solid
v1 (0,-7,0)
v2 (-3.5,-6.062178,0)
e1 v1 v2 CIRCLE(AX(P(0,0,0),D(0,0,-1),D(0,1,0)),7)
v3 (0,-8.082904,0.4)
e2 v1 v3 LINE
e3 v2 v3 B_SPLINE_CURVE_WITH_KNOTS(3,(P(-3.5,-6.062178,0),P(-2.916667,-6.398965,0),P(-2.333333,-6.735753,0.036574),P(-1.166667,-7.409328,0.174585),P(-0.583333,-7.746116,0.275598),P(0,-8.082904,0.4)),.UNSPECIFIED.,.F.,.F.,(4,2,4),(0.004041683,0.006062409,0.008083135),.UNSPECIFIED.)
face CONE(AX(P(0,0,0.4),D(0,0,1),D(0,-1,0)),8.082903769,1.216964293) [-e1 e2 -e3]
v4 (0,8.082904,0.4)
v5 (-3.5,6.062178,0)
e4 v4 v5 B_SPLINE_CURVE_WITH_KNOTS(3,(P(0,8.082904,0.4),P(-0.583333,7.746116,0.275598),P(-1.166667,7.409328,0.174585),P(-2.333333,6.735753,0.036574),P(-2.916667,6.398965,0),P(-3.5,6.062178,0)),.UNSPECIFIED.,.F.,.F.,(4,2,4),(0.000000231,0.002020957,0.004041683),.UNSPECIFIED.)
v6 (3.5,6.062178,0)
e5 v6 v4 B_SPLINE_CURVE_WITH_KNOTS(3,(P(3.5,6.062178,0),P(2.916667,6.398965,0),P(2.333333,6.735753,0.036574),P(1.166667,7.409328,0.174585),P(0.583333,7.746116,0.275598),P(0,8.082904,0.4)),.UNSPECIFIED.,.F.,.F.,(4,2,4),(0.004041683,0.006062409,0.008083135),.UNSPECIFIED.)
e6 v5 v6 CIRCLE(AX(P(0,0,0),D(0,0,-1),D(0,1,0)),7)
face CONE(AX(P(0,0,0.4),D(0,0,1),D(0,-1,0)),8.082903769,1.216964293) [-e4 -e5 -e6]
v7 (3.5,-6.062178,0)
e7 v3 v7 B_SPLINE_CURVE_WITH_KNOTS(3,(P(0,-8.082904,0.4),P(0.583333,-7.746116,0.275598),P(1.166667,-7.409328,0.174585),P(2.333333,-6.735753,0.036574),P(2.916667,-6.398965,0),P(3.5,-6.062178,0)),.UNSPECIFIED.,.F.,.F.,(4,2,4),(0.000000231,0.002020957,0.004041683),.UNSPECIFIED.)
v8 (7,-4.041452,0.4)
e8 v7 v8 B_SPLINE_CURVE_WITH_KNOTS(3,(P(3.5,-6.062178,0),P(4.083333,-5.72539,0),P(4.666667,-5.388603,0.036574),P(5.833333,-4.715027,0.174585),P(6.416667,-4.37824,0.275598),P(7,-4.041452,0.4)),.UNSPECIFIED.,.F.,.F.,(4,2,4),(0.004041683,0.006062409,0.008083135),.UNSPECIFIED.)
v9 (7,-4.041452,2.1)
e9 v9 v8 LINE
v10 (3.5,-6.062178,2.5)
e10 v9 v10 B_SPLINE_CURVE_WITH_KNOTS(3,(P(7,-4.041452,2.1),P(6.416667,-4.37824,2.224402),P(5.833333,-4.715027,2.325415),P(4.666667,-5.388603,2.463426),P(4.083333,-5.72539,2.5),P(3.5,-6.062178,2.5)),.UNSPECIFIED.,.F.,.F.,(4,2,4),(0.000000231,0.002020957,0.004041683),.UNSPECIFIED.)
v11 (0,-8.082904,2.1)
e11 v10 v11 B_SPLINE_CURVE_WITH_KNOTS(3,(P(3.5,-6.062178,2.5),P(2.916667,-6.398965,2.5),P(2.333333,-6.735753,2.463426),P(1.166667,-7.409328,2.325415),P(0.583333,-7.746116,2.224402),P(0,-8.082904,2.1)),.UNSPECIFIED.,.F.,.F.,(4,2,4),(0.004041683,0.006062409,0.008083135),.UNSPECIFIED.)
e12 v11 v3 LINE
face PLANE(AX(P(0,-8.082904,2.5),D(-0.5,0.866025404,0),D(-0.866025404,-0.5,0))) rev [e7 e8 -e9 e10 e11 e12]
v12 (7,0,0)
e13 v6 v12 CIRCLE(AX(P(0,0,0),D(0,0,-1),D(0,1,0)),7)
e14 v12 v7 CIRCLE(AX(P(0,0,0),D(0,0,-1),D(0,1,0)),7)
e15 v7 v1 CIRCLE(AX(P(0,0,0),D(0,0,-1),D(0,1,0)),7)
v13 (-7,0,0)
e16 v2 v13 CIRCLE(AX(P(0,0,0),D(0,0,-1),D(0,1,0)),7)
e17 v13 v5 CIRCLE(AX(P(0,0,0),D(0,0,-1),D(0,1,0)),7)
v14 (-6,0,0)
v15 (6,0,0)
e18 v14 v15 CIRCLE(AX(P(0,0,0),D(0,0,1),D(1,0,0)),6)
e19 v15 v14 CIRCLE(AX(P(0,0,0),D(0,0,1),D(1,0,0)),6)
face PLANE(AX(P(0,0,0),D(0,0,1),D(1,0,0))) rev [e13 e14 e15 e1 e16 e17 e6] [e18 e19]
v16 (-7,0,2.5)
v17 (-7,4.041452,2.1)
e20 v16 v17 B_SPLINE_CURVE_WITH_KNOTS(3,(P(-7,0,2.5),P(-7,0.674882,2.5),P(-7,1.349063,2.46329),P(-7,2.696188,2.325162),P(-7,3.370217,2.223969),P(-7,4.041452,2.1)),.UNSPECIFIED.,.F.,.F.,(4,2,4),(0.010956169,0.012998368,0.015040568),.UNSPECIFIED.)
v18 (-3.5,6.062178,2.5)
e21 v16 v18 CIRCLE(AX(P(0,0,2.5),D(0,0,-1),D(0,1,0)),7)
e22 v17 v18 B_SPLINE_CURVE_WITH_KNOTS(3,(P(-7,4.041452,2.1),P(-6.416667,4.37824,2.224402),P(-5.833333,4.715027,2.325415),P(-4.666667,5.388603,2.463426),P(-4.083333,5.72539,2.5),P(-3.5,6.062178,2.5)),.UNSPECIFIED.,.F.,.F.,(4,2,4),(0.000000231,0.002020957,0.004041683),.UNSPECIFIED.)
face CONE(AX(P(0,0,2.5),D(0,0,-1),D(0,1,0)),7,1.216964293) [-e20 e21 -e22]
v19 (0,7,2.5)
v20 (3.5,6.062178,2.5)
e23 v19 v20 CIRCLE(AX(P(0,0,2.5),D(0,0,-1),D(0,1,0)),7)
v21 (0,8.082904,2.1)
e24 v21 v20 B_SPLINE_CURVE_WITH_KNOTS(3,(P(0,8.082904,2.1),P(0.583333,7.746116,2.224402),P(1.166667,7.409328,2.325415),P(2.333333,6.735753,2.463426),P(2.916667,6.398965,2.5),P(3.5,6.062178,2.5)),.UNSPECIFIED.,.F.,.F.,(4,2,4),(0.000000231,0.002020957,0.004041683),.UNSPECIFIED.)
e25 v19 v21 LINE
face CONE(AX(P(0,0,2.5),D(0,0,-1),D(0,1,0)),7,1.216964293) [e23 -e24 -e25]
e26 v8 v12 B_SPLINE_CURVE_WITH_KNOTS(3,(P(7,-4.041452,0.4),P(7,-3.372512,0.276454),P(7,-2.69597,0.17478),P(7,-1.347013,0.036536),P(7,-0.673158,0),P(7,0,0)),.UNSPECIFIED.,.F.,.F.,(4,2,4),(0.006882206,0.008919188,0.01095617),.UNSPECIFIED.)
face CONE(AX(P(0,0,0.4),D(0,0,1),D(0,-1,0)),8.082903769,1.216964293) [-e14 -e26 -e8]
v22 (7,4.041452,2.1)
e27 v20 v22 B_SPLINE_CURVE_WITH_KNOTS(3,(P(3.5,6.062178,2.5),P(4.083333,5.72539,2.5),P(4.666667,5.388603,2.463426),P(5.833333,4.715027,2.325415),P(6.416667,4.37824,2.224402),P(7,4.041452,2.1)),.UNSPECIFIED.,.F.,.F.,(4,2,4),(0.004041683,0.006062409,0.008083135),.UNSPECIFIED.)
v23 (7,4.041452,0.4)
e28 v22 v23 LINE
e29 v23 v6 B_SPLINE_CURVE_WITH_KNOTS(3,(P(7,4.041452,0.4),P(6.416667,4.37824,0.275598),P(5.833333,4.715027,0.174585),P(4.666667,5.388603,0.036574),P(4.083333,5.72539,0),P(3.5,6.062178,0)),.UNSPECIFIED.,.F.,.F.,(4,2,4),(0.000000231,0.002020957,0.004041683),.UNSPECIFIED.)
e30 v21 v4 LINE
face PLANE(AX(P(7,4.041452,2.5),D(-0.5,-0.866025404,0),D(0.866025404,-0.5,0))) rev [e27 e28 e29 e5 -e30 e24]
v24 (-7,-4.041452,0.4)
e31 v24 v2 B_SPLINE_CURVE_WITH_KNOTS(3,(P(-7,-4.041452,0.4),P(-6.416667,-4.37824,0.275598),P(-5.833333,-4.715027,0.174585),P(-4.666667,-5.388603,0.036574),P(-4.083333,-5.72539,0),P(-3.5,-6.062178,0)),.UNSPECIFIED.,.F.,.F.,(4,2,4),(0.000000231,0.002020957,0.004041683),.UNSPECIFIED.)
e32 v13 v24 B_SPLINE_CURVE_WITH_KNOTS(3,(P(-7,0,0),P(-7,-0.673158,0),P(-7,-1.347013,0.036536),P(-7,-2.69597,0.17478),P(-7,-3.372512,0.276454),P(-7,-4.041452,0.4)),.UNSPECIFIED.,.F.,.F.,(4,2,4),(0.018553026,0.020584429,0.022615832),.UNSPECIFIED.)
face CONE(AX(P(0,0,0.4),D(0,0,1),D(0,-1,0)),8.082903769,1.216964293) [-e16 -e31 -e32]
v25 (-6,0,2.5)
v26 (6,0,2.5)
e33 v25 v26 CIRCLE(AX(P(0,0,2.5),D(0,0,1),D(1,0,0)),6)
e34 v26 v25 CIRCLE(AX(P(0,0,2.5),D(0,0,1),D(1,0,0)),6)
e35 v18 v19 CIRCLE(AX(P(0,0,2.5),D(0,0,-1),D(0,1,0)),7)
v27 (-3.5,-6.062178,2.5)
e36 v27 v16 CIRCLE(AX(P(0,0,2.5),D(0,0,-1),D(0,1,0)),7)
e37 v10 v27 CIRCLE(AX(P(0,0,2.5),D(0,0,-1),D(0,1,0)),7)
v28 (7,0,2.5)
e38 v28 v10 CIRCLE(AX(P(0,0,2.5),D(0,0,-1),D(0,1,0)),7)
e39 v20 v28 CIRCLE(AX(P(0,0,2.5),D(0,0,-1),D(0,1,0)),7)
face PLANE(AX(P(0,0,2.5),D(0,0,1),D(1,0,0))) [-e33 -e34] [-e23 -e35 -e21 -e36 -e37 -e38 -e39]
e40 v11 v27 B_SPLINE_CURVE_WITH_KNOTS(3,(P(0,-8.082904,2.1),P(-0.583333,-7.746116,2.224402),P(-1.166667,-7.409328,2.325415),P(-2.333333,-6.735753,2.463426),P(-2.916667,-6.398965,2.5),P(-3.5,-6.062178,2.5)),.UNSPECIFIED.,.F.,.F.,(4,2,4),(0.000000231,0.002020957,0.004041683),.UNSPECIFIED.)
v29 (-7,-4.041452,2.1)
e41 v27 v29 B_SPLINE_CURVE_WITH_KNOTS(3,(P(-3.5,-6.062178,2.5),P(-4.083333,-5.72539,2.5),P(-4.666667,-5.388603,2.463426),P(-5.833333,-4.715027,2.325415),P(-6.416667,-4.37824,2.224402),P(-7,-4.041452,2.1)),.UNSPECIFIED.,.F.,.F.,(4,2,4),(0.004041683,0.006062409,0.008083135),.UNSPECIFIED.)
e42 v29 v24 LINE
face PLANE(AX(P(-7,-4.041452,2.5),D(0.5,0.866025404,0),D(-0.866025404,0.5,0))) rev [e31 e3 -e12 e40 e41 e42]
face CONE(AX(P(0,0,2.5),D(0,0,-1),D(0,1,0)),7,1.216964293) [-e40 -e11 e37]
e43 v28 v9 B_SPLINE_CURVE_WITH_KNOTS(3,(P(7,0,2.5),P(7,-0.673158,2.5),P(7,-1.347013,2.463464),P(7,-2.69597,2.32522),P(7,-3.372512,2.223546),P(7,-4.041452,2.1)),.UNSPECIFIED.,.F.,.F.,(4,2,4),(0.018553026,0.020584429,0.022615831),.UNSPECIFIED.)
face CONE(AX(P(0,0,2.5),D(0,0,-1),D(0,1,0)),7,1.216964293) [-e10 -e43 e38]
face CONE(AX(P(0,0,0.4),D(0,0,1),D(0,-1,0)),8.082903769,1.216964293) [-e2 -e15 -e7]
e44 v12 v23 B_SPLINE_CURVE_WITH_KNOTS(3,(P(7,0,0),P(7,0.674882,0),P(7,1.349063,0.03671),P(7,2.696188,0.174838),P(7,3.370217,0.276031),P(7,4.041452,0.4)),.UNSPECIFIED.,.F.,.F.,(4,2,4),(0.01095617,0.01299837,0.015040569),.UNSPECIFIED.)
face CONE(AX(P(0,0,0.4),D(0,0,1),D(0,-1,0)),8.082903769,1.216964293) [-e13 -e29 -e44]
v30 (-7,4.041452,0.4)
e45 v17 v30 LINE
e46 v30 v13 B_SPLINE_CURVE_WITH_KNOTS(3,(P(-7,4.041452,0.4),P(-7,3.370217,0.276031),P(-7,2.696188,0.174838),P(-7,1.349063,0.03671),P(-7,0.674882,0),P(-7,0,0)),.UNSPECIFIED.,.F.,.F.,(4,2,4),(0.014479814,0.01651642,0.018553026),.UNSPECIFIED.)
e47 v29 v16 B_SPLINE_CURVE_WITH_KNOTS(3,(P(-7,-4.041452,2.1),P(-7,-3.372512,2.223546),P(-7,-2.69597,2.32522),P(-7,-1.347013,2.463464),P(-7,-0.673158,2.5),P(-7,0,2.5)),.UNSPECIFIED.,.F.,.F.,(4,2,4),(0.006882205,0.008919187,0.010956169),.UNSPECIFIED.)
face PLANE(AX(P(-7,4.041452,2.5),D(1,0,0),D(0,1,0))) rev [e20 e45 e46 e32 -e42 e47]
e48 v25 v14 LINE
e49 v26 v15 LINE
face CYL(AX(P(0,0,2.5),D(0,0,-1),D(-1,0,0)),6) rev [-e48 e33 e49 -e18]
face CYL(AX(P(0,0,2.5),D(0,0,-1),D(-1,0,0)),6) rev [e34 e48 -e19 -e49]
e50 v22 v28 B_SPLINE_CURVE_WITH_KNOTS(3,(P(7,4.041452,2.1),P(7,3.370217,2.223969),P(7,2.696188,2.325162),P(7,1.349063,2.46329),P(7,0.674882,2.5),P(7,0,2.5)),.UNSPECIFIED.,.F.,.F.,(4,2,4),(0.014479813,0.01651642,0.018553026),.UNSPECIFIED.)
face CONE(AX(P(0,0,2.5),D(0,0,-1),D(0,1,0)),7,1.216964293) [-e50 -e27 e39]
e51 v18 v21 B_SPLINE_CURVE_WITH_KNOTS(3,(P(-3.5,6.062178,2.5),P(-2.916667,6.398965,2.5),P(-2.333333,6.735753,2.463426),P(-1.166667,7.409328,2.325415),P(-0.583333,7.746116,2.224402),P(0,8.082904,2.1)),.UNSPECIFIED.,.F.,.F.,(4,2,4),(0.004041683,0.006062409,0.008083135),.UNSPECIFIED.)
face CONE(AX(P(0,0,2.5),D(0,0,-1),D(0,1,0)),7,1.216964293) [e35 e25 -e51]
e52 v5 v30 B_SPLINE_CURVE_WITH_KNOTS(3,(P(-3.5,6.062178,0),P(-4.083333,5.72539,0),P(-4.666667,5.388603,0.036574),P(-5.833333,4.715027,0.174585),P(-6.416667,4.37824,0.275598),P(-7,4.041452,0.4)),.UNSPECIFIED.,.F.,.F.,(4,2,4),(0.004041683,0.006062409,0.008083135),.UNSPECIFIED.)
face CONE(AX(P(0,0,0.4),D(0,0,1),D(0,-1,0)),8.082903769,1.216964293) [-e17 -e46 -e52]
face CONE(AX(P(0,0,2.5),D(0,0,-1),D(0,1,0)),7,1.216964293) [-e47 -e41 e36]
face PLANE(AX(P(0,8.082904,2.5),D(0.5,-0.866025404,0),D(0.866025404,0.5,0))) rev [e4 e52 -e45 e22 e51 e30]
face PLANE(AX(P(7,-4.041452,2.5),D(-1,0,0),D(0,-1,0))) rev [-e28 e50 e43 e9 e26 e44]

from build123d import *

# Parameters (mm, degrees)
SKETCH1_R           = 6
BOSS_EXTRUDE1_DEPTH = 2.5


with BuildPart() as part:
    # Sketch1 → Boss-Extrude1 (new body)
    with BuildSketch(Plane.XY):
        Polygon((0, 8.082903769), (-7, 4.041451884), (-7, -4.041451884), (0, -8.082903769), (7, -4.041451884), (7, 4.041451884), align=None)
        Circle(SKETCH1_R, mode=Mode.SUBTRACT)
    extrude(amount=BOSS_EXTRUDE1_DEPTH)

    # Sketch3 → Cut-Revolve1 (revolve, cut)
    with BuildSketch(Plane(origin=(0, 0, 0), x_dir=(0, 0, -1), z_dir=(1, 0, 0))):
        Polygon((-2.5, 8.082903769), (-2.1, 8.082903769), (-2.5, 7), align=None)
        Polygon((0, 8.082903769), (-0.4, 8.082903769), (0, 7), align=None)
    revolve(axis=Axis((0, 0, 0), (0, 0, 1)), mode=Mode.SUBTRACT)


solid = part.part
